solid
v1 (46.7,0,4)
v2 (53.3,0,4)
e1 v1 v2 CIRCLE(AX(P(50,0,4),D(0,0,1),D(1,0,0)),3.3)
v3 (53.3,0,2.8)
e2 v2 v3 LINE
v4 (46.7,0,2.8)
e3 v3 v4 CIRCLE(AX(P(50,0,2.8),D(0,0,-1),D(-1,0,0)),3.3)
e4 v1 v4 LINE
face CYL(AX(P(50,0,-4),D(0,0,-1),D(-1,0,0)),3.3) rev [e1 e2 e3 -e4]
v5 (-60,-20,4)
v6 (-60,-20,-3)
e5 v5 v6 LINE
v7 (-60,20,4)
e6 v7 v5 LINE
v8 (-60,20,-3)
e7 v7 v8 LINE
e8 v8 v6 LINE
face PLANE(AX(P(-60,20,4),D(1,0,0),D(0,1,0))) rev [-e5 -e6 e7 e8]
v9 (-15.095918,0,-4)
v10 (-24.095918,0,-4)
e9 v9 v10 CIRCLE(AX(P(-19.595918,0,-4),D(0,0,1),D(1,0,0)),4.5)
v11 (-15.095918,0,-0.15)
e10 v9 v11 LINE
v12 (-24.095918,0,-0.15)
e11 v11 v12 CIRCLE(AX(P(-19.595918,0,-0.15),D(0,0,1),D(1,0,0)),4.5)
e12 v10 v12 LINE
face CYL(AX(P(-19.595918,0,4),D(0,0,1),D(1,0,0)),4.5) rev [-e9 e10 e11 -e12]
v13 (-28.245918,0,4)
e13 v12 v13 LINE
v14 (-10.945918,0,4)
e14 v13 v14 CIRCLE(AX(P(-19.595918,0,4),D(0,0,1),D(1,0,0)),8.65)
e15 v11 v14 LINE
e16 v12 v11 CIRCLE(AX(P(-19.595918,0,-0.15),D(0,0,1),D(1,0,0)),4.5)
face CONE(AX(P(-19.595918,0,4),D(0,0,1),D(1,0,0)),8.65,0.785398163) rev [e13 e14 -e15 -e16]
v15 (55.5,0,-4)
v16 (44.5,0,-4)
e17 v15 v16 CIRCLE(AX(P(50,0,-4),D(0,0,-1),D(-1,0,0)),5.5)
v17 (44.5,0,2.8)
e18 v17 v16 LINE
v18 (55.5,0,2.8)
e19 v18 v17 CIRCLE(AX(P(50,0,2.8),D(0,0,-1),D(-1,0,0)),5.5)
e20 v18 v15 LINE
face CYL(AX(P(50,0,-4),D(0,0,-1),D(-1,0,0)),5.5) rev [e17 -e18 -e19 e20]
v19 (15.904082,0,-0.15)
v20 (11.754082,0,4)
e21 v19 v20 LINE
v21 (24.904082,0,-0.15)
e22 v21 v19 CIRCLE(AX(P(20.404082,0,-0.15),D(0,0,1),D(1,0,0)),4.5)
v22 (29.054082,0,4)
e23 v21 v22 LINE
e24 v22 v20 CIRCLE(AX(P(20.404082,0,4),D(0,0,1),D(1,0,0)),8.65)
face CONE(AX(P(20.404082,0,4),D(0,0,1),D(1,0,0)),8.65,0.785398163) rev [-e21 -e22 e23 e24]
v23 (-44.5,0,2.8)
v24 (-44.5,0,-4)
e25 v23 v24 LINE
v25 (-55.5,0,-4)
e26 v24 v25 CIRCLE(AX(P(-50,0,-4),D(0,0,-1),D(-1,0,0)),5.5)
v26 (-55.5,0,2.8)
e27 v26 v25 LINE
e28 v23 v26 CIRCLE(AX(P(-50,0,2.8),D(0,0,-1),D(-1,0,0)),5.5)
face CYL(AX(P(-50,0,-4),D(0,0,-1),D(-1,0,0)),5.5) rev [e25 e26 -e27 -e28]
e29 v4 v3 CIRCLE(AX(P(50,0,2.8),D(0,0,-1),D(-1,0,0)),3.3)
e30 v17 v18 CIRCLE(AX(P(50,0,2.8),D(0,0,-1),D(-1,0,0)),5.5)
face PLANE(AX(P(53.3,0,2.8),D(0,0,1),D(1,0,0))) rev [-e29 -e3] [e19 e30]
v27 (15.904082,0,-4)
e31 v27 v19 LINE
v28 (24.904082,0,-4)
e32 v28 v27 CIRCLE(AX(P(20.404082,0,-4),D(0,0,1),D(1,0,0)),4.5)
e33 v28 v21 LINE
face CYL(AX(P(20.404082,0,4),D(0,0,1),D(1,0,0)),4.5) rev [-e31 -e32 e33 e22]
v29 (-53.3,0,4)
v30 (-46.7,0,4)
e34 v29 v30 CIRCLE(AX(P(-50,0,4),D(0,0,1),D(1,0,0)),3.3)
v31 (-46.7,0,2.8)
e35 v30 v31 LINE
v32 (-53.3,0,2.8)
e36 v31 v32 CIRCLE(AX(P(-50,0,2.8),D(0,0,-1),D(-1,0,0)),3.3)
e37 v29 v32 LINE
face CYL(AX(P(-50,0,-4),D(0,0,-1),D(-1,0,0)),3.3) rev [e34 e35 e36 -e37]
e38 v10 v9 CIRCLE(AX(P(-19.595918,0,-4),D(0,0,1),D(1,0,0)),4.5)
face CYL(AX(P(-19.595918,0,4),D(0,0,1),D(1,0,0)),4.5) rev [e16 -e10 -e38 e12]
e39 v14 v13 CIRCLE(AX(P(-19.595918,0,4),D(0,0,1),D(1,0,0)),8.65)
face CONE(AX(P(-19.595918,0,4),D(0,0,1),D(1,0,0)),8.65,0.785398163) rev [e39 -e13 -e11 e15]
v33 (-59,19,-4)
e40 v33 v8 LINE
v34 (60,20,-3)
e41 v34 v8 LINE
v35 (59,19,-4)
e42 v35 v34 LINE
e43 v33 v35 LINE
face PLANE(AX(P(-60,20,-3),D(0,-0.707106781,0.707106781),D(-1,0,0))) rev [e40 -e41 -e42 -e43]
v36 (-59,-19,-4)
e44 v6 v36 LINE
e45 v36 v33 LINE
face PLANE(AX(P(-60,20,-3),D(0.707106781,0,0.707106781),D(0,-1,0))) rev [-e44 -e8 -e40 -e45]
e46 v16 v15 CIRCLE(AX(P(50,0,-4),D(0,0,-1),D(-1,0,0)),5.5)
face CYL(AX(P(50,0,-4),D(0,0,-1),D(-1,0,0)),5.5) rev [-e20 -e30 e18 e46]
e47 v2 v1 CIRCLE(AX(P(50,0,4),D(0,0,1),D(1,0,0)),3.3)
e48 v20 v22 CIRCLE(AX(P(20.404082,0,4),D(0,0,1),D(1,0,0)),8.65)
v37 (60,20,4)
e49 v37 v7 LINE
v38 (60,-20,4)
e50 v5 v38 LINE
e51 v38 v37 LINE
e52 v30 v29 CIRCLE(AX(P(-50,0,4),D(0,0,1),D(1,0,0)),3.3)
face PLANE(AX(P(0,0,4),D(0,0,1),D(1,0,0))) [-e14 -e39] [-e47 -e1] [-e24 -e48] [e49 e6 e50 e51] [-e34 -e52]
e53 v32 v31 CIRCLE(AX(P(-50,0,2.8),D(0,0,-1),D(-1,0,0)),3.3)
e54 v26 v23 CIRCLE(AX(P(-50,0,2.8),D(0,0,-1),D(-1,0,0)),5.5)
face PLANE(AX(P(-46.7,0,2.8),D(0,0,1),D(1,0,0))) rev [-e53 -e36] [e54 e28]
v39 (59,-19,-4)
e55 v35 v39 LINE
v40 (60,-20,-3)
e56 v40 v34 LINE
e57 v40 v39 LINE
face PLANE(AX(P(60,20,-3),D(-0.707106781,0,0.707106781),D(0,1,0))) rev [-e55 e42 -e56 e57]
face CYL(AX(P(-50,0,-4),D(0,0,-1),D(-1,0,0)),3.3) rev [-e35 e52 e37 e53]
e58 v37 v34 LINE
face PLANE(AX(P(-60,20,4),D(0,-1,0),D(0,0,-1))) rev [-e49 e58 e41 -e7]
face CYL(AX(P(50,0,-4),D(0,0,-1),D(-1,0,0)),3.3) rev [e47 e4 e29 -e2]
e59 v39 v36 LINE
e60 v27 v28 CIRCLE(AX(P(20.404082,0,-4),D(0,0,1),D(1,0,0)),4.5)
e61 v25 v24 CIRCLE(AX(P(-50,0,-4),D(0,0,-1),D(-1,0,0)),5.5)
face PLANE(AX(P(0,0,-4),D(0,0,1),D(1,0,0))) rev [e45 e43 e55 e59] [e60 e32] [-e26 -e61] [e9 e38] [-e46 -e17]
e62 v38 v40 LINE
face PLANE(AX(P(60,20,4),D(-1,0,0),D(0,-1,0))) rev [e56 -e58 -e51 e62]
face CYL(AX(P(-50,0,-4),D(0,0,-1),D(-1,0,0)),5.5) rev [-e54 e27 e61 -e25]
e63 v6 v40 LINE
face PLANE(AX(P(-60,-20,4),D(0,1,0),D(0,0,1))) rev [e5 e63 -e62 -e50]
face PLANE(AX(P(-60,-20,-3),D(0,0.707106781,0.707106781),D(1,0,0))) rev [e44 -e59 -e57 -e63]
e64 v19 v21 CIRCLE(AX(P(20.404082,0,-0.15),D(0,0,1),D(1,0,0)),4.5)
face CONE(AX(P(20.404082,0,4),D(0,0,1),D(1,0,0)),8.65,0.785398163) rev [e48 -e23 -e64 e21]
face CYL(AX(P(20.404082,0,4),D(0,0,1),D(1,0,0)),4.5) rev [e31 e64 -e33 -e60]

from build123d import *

# Parameters (mm, degrees)
SKETCH_1_W                  = 120
SKETCH_1_H                  = 40
EXTRUDE_1_DEPTH             = 4
HOLE_WIZARD_1_D             = 9
HOLE_WIZARD_1_DEPTH         = 10
HOLE_WIZARD_1_CSINK_D       = 17.3
HOLE_WIZARD_1_CSINK_ANGLE   = 90
HOLE_WIZARD_1_TIP           = 2.703872786
HOLE_WIZARD_1_2_D           = 6.6
HOLE_WIZARD_1_2_DEPTH       = 10
HOLE_WIZARD_1_2_CBORE_D     = 11
HOLE_WIZARD_1_2_CBORE_DEPTH = 6.8
HOLE_WIZARD_1_2_TIP         = 1.982840043
CHAMFER_1_SIZE              = 1


with BuildPart() as part:
    # 草图1 → 凸台-拉伸1 (new, symmetric)
    with BuildSketch(Plane.XY):
        Rectangle(SKETCH_1_W, SKETCH_1_H)
    extrude(amount=EXTRUDE_1_DEPTH, both=True)

    # Hole Wizard 1
    with Locations(Plane(origin=(-19.595917942, 0, 4), x_dir=(1, 0, 0), z_dir=(0, 0, 1))):
        with Locations((0, 0), (40, 0)):
            CounterSinkHole(HOLE_WIZARD_1_D / 2, HOLE_WIZARD_1_CSINK_D / 2, depth=HOLE_WIZARD_1_DEPTH, counter_sink_angle=HOLE_WIZARD_1_CSINK_ANGLE)
            with Locations((0, 0, -(HOLE_WIZARD_1_DEPTH + HOLE_WIZARD_1_TIP / 2))):  # 118° drill point
                Cone(0, HOLE_WIZARD_1_D / 2, HOLE_WIZARD_1_TIP, mode=Mode.SUBTRACT)

    # Hole Wizard 1 2
    with Locations(Plane(origin=(50, 0, -4), x_dir=(-1, 0, 0), z_dir=(0, 0, -1))):
        with Locations((0, 0), (100, 0)):
            CounterBoreHole(HOLE_WIZARD_1_2_D / 2, HOLE_WIZARD_1_2_CBORE_D / 2, HOLE_WIZARD_1_2_CBORE_DEPTH, depth=HOLE_WIZARD_1_2_DEPTH)
            with Locations((0, 0, -(HOLE_WIZARD_1_2_DEPTH + HOLE_WIZARD_1_2_TIP / 2))):  # 118° drill point
                Cone(0, HOLE_WIZARD_1_2_D / 2, HOLE_WIZARD_1_2_TIP, mode=Mode.SUBTRACT)

    # 倒角1
    chamfer_1_edges = [part.edges().sort_by_distance(p)[0] for p in [
        (0, -20, -4),
        (-60, 0, -4),
        (0, 20, -4),
        (60, 0, -4),
    ]]
    chamfer(chamfer_1_edges, length=CHAMFER_1_SIZE)


solid = part.part
